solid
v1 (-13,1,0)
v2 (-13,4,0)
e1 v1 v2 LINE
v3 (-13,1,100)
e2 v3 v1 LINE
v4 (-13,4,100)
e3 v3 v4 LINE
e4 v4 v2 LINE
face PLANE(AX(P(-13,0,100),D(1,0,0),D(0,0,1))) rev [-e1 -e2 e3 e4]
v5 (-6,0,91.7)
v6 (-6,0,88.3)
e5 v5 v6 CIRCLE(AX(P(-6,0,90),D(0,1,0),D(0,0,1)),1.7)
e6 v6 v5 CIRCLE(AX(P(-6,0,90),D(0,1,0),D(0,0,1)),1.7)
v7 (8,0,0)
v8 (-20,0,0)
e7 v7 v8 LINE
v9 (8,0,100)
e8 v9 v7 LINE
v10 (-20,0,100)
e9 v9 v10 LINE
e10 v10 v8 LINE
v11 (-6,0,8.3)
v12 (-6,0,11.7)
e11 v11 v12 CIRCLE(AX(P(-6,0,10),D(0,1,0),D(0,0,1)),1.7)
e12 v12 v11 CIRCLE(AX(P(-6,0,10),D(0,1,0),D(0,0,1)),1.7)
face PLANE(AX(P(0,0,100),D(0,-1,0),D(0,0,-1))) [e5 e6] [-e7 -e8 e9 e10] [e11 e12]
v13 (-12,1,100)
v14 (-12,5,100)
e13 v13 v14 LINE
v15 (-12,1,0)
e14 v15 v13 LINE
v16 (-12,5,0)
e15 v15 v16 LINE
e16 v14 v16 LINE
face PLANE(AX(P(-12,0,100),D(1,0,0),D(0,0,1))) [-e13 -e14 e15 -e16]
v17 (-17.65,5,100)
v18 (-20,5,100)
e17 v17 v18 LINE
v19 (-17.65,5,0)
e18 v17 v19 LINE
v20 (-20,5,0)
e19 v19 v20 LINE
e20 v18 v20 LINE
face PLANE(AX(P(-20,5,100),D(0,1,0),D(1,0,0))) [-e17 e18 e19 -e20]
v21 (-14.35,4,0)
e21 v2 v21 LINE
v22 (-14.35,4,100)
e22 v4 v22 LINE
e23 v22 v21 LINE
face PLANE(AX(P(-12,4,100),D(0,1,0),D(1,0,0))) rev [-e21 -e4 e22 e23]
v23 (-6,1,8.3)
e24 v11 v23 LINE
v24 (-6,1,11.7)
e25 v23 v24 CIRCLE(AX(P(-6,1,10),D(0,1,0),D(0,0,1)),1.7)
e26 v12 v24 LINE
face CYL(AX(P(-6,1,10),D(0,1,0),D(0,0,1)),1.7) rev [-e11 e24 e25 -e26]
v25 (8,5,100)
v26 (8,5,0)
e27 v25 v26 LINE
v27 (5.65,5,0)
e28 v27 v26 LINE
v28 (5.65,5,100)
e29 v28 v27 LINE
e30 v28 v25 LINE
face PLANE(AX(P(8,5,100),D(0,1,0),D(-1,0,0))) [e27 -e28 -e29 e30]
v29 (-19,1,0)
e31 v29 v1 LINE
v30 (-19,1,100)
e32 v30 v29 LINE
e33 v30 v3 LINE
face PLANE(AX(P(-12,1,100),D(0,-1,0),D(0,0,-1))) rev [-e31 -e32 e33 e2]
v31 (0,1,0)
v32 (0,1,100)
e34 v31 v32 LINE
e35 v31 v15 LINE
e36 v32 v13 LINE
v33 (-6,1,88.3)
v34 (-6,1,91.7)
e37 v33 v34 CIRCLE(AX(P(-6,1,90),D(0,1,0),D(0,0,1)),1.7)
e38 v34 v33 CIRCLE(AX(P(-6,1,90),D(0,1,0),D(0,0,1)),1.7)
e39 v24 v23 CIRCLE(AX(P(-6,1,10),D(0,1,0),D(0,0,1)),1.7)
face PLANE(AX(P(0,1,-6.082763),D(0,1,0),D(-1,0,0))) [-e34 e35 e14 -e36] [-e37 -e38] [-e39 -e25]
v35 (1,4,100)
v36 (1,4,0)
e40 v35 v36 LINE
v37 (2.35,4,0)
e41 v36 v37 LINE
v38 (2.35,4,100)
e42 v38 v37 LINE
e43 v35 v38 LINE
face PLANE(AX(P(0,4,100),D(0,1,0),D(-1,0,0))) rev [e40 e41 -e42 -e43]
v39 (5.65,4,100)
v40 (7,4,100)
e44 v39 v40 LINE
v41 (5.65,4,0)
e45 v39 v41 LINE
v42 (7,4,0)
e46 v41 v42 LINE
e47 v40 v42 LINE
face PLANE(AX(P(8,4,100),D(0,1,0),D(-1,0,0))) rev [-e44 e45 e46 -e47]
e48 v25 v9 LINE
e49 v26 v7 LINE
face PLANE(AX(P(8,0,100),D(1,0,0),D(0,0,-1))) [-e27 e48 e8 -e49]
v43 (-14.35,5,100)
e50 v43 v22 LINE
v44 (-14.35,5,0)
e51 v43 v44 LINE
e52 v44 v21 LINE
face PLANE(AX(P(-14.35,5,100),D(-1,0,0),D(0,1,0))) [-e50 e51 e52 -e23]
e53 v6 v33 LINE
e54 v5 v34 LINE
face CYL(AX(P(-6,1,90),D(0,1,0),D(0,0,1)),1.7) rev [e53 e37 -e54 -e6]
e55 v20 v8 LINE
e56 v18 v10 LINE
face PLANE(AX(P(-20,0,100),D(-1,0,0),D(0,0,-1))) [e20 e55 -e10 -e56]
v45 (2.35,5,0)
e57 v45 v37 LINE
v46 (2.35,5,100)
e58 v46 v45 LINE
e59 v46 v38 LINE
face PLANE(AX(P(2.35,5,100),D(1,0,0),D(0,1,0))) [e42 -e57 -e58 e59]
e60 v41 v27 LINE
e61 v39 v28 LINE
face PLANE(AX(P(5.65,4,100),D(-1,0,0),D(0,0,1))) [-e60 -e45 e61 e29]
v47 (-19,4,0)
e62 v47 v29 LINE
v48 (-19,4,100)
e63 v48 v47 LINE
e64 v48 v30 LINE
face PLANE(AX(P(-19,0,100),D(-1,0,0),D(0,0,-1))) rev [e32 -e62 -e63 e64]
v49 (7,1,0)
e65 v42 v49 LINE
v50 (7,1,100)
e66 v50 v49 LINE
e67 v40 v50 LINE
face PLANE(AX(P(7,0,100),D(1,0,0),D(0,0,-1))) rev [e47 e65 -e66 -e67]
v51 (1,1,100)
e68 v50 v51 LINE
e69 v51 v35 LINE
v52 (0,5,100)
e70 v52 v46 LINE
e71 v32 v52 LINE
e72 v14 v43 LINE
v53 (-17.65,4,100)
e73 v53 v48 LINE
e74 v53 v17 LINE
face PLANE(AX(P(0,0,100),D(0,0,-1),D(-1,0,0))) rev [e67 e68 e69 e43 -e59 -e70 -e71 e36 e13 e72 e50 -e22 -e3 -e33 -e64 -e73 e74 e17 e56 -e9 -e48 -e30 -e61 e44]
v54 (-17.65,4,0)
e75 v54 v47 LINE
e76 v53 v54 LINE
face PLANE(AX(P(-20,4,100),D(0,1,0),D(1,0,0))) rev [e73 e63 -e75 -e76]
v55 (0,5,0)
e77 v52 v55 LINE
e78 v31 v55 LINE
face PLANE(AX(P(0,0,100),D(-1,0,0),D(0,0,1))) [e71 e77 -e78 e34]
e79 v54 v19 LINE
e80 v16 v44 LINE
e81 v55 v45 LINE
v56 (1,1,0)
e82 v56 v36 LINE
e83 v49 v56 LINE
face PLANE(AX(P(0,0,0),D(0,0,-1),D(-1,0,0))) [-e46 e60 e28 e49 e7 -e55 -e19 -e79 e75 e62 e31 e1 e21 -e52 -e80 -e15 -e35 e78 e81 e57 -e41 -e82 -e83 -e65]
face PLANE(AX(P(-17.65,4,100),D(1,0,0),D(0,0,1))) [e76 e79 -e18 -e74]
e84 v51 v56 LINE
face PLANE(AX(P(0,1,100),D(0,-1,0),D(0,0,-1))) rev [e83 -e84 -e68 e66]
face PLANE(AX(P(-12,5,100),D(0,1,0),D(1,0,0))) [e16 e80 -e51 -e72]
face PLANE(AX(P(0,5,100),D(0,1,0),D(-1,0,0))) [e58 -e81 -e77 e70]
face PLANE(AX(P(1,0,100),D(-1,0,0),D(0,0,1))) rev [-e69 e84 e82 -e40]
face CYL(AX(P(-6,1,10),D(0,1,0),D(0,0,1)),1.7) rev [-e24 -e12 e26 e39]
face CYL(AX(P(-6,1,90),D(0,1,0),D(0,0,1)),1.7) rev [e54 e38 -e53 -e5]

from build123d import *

# Parameters (mm, degrees)
EXTRUDE_1_DEPTH    = 100
SKETCH_2_W         = 6
SKETCH_2_H         = 1
EXTRUDE_2_DEPTH    = 100
HOLE_WIZARD_M3_1_D = 3.4


with BuildPart() as part:
    # 草图1 → 拉伸-薄壁1 (new body)
    with BuildSketch(Plane.XY):
        Polygon((2.35, 5), (0, 5), (0, 0), (8, 0), (8, 5), (5.65, 5), (5.65, 4), (7, 4), (7, 1), (1, 1), (1, 4), (2.35, 4), align=None)
    extrude(amount=EXTRUDE_1_DEPTH)

    # 草图2 → 拉伸-薄壁2 (add)
    with BuildSketch(Plane.XY.offset(100)):
        with Locations((-3, 0.5)):
            Rectangle(SKETCH_2_W, SKETCH_2_H)
    extrude(amount=-EXTRUDE_2_DEPTH)

    # 镜向1: part across plane


with BuildPart() as part_1:
    add(part.part)
    add(part.part.mirror(Plane(origin=(-6, 0, -6.08276253), x_dir=(0, 0, 1), z_dir=(1, 0, 0))))

    # M3 间隙孔1 (through all)
    with Locations(Plane(origin=(0, 1, 0), x_dir=(1, 0, 0), z_dir=(0, 1, 0))):
        with Locations((-6, -90), (-6, -10)):
            Hole(HOLE_WIZARD_M3_1_D / 2)


solid = part_1.part
